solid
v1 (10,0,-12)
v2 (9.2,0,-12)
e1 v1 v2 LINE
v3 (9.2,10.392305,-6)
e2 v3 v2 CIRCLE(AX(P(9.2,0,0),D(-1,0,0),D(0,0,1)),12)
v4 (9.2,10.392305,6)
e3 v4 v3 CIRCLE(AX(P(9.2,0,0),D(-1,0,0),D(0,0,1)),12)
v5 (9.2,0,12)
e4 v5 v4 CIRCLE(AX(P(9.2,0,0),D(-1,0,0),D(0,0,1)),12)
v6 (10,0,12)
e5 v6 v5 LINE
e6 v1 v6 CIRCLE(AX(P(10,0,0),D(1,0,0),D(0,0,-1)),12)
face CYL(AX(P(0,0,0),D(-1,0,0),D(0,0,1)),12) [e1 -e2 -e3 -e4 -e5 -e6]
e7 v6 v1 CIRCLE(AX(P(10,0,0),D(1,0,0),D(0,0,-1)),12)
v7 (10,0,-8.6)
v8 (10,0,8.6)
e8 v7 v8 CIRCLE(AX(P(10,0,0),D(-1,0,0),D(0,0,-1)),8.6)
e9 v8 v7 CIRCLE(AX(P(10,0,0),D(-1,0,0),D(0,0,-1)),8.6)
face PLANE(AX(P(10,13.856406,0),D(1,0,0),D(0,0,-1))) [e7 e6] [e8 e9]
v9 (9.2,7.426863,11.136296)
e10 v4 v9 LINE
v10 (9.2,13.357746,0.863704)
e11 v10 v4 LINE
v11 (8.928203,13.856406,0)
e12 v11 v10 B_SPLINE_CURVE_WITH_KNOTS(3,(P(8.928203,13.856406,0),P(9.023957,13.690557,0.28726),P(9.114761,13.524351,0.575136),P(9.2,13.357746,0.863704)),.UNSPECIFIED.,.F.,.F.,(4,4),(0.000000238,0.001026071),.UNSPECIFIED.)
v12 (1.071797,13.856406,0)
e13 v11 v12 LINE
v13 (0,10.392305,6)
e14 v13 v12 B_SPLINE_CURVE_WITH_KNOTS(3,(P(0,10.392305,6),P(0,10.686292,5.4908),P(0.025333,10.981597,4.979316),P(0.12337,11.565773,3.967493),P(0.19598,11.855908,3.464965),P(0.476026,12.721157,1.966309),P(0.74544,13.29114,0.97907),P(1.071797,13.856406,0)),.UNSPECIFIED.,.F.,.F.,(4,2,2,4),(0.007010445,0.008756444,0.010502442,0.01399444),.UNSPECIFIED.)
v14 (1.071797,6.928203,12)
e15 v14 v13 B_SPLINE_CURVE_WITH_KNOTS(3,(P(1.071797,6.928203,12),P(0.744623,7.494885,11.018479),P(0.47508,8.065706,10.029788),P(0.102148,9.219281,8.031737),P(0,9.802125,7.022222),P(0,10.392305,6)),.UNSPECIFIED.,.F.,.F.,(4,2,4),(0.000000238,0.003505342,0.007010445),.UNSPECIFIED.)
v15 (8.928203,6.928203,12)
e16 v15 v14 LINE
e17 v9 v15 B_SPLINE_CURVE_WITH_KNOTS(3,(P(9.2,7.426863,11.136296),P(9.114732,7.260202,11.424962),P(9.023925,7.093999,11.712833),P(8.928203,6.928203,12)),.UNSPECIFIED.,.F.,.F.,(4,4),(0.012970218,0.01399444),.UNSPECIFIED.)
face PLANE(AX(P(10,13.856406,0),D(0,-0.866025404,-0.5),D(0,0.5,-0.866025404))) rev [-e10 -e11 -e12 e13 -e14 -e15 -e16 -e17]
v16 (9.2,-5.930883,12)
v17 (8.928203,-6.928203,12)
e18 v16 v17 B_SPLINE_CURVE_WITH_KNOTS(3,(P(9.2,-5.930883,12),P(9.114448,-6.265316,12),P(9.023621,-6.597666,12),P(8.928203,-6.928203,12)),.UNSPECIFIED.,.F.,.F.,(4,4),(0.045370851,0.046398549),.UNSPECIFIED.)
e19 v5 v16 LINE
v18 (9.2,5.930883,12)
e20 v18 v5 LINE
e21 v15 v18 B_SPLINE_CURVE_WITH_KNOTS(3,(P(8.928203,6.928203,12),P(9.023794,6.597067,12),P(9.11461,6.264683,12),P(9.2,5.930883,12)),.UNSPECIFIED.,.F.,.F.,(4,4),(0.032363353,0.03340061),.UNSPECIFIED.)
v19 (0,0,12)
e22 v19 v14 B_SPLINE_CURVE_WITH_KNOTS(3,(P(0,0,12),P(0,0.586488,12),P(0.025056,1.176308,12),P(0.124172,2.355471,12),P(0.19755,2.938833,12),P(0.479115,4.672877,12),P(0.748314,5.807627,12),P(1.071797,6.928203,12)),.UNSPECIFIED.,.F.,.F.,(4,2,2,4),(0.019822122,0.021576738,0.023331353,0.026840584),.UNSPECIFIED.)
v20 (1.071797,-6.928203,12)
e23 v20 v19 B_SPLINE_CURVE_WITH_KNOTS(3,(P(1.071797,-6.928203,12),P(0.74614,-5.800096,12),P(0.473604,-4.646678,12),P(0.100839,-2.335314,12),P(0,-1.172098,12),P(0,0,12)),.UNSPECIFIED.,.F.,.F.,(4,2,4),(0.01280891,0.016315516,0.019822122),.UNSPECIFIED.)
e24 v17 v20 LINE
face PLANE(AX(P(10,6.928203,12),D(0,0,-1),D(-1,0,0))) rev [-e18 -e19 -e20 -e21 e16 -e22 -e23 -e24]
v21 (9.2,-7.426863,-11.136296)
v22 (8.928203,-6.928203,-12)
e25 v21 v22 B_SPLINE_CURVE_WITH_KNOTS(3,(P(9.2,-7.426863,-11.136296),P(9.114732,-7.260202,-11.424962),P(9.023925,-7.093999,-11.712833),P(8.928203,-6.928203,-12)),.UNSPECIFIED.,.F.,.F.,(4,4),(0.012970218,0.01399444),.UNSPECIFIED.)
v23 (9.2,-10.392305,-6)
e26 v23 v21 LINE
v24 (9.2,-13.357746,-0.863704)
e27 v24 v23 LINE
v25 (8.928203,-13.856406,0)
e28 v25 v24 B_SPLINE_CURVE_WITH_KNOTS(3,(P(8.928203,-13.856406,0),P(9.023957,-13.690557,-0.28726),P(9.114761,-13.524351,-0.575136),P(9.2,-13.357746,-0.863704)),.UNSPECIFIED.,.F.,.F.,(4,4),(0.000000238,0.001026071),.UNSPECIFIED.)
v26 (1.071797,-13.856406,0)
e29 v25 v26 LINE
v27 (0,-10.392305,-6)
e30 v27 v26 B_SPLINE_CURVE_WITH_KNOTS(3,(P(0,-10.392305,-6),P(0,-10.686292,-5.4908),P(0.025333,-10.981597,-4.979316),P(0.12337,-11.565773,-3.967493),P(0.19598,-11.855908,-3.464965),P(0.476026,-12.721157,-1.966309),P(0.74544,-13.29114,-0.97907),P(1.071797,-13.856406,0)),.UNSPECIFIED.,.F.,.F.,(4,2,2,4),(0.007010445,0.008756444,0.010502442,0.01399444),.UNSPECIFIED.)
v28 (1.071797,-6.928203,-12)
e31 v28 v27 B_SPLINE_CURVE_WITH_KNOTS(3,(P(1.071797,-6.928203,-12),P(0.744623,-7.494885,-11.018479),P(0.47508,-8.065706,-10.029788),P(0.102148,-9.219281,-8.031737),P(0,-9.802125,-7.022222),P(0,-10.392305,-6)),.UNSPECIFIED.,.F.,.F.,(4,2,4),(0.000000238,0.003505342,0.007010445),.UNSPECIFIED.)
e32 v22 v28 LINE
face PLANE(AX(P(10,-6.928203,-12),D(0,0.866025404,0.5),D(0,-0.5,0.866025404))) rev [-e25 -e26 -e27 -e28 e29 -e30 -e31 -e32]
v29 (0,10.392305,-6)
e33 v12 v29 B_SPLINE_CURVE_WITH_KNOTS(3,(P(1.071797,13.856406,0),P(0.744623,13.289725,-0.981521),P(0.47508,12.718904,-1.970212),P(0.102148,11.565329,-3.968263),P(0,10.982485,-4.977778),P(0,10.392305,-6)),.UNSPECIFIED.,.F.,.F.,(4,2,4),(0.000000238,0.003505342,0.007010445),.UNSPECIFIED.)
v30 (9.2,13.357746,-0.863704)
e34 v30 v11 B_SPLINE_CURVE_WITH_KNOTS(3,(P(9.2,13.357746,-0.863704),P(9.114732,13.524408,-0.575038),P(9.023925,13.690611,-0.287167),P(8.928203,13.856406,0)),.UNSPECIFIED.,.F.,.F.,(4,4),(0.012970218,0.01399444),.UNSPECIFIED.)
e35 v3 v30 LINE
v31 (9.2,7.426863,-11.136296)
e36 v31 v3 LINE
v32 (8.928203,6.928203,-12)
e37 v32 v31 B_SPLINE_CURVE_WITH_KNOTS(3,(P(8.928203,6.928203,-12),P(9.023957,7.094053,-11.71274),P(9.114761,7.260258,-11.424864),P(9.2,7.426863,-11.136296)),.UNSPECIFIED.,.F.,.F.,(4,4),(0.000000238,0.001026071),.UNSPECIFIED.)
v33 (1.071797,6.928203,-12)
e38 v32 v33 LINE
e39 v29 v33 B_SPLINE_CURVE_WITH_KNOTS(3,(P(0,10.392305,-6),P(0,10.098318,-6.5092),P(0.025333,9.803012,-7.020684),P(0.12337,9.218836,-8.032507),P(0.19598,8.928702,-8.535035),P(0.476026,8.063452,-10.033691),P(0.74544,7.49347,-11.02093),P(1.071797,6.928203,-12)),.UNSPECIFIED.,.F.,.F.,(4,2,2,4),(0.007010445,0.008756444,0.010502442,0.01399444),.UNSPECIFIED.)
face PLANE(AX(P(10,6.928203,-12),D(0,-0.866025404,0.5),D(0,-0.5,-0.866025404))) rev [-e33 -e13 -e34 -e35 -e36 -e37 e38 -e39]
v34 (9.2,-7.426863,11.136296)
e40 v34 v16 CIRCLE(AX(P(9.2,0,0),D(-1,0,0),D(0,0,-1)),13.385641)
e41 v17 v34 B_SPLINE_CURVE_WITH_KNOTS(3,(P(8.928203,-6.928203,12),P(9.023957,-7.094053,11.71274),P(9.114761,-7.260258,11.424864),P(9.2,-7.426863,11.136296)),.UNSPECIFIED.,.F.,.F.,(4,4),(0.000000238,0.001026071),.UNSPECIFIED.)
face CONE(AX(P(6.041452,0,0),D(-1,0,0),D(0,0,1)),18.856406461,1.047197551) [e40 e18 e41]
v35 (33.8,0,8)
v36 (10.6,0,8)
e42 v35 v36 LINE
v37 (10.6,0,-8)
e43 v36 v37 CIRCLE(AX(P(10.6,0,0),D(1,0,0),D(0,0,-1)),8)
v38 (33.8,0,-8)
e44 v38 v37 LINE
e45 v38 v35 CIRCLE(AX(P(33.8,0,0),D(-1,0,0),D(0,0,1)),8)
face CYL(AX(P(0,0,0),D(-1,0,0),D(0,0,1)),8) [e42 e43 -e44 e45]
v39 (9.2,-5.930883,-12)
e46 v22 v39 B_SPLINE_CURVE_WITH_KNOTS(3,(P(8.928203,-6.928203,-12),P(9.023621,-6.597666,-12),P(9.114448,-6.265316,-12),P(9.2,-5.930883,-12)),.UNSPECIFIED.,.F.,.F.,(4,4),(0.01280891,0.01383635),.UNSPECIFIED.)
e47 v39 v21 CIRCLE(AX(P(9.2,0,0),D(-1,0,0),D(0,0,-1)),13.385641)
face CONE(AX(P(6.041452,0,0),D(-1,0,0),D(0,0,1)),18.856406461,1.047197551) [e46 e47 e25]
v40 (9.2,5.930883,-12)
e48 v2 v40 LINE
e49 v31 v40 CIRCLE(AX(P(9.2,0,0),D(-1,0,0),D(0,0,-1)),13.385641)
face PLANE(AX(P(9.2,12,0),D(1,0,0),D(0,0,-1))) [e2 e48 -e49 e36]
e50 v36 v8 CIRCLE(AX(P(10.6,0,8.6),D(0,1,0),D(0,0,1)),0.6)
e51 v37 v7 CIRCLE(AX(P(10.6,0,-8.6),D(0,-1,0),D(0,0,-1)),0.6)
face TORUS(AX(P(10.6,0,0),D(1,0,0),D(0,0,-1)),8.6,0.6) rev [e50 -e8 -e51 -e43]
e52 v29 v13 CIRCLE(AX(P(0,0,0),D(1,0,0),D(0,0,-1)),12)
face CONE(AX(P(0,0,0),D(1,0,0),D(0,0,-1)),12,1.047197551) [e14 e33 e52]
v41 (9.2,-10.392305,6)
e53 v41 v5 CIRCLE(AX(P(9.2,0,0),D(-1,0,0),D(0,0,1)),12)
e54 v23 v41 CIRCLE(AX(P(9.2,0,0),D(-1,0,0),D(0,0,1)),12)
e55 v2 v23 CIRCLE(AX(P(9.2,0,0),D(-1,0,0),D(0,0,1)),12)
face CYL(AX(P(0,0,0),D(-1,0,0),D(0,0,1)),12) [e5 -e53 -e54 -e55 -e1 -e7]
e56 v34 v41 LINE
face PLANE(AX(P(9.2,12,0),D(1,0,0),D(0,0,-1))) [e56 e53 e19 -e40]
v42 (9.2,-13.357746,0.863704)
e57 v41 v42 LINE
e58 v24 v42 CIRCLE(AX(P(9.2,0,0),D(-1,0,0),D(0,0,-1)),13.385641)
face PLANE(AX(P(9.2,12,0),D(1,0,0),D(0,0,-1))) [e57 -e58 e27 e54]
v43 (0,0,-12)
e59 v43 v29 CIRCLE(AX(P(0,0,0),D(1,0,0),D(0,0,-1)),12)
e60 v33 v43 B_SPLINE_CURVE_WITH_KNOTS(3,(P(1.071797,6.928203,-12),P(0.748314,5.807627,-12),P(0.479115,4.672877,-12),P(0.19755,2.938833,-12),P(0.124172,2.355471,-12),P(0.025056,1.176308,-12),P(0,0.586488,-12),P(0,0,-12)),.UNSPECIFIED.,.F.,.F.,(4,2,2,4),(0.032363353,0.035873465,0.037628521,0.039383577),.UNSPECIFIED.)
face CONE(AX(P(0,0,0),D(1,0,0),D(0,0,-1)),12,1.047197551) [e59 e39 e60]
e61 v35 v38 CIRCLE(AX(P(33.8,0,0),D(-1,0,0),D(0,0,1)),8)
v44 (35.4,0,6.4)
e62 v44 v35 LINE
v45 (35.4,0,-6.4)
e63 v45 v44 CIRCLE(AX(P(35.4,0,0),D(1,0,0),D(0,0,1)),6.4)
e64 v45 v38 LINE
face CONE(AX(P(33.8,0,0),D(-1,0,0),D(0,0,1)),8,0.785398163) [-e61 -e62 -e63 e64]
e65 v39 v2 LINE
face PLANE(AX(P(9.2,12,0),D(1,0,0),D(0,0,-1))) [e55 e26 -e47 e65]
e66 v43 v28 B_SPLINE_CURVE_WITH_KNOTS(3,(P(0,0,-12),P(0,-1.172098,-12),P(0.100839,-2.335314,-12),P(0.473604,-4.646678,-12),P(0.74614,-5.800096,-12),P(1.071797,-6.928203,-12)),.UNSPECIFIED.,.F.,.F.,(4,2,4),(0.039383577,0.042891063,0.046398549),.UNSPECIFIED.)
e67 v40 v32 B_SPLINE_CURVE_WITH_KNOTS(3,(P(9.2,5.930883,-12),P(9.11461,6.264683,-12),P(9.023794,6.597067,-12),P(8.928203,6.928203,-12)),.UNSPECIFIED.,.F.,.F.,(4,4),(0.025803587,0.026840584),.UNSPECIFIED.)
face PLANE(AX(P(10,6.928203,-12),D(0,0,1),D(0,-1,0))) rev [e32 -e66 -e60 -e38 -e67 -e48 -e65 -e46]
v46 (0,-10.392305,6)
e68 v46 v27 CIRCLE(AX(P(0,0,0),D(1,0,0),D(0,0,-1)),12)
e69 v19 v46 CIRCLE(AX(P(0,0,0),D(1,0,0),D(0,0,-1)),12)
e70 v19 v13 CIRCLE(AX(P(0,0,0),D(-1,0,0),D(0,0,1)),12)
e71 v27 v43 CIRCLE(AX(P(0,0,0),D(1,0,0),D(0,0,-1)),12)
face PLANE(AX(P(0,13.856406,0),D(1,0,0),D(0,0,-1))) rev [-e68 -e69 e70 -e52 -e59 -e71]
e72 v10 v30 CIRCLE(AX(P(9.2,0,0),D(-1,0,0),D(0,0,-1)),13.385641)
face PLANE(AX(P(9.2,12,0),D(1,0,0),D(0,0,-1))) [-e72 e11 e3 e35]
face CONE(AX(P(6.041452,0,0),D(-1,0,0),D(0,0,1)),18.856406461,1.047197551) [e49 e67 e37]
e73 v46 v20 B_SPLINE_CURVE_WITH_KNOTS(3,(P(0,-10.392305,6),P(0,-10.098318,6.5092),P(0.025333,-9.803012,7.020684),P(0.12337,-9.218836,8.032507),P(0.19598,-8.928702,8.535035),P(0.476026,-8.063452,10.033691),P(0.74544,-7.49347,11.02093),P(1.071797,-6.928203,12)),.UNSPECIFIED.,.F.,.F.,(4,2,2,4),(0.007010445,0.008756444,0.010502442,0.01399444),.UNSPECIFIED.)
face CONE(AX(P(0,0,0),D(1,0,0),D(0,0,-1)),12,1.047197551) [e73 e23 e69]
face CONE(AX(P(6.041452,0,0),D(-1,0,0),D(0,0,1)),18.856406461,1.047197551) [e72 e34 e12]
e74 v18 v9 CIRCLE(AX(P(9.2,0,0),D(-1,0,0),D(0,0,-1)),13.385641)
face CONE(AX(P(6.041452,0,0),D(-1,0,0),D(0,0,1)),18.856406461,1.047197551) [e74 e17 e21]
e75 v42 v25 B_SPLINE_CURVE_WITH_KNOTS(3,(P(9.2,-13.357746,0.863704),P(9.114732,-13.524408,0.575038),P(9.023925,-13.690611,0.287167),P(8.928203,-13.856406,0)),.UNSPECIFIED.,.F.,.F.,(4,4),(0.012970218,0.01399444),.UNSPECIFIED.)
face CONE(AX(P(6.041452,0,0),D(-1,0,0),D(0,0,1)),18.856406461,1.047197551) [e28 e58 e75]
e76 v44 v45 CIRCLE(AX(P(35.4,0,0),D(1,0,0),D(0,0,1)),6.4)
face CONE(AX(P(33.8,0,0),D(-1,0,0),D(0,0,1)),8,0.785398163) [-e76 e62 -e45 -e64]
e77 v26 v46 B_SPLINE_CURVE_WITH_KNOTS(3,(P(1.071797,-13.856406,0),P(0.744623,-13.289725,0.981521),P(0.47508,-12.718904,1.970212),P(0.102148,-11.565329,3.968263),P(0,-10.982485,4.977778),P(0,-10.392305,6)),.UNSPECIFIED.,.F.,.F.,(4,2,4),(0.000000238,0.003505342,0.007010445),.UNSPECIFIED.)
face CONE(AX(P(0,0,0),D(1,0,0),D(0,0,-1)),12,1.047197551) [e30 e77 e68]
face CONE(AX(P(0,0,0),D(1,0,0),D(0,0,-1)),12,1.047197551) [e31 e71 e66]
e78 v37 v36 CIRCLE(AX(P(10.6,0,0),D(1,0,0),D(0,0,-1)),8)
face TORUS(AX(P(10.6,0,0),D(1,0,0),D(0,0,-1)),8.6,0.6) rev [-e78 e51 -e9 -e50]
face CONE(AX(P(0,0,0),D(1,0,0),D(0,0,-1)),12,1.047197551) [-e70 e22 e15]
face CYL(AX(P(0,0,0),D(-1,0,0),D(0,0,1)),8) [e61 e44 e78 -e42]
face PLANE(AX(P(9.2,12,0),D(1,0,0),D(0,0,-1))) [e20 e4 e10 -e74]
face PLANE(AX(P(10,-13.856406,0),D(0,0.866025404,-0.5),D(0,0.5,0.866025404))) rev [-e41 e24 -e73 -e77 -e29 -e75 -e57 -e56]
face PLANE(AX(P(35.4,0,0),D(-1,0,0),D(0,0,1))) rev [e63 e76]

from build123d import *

# Parameters (mm, degrees)
BASE_EXTRUDE_DEPTH = 10
SKETCH4_W          = 0.8
SKETCH4_H          = 11.856406461
CHAMFER_2_SIZE     = 1.6
FILLET_2_R         = 0.6


with BuildPart() as part:
    # Sketch1 → Base-Extrude (new body)
    with BuildSketch(Plane(origin=(0, 0, 0), x_dir=(0, 0, -1), z_dir=(1, 0, 0))):
        Polygon((12, 6.92820323), (12, -6.92820323), (0, -13.856406461), (-12, -6.92820323), (-12, 6.92820323), (0, 13.856406461), align=None)
    extrude(amount=BASE_EXTRUDE_DEPTH)

    # Sketch2 → Boss-Revolve1 (revolve)
    with BuildSketch(Plane.XY, mode=Mode.PRIVATE) as boss_revolve1_sk:
        Polygon((0, 0), (35.4, 0), (35.4, 6.268), (35.4, 8), (27.8072, 8), (0, 8), align=None)
    revolve(boss_revolve1_sk.sketch.rotate(Axis((0, 0, 0), (1, 0, 0)), 90), axis=Axis((0, 0, 0), (1, 0, 0)))

    # Sketch3 → Cut-Revolve1 (revolve, cut)
    with BuildSketch(Plane.XY):
        Polygon((0, 12), (3.958548116, 18.856406461), (3.958548116, 23.856406461), (-10, 23.856406461), (-10, 12), align=None)
    revolve(axis=Axis((0, 0, 0), (1, 0, 0)), mode=Mode.SUBTRACT)

    # Sketch5 → Cut-Revolve2 (revolve, cut)
    with BuildSketch(Plane.XY):
        Polygon((10, 12), (6.041451884, 18.856406461), (6.041451884, 23.856406461), (16.041451884, 23.856406461), (16.041451884, 12), align=None)
    revolve(axis=Axis((0, 0, 0), (1, 0, 0)), mode=Mode.SUBTRACT)

    # Sketch4 → Cut-Revolve3 (revolve, cut)
    with BuildSketch(Plane.XY, mode=Mode.PRIVATE) as cut_revolve3_sk:
        with Locations((9.6, 17.928203231)):
            Rectangle(SKETCH4_W, SKETCH4_H)
    revolve(cut_revolve3_sk.sketch.rotate(Axis((0, 0, 0), (1, 0, 0)), 270), axis=Axis((0, 0, 0), (1, 0, 0)), mode=Mode.SUBTRACT)

    # Chamfer 2
    chamfer_2_edges = [part.edges().sort_by_distance(p)[0] for p in [
        (35.4, 0, -8),
    ]]
    chamfer(chamfer_2_edges, length=CHAMFER_2_SIZE)

    # Fillet 2
    fillet_2_edges = [part.edges().sort_by_distance(p)[0] for p in [
        (10, 0, -8),
    ]]
    fillet(fillet_2_edges, radius=FILLET_2_R)


solid = part.part
